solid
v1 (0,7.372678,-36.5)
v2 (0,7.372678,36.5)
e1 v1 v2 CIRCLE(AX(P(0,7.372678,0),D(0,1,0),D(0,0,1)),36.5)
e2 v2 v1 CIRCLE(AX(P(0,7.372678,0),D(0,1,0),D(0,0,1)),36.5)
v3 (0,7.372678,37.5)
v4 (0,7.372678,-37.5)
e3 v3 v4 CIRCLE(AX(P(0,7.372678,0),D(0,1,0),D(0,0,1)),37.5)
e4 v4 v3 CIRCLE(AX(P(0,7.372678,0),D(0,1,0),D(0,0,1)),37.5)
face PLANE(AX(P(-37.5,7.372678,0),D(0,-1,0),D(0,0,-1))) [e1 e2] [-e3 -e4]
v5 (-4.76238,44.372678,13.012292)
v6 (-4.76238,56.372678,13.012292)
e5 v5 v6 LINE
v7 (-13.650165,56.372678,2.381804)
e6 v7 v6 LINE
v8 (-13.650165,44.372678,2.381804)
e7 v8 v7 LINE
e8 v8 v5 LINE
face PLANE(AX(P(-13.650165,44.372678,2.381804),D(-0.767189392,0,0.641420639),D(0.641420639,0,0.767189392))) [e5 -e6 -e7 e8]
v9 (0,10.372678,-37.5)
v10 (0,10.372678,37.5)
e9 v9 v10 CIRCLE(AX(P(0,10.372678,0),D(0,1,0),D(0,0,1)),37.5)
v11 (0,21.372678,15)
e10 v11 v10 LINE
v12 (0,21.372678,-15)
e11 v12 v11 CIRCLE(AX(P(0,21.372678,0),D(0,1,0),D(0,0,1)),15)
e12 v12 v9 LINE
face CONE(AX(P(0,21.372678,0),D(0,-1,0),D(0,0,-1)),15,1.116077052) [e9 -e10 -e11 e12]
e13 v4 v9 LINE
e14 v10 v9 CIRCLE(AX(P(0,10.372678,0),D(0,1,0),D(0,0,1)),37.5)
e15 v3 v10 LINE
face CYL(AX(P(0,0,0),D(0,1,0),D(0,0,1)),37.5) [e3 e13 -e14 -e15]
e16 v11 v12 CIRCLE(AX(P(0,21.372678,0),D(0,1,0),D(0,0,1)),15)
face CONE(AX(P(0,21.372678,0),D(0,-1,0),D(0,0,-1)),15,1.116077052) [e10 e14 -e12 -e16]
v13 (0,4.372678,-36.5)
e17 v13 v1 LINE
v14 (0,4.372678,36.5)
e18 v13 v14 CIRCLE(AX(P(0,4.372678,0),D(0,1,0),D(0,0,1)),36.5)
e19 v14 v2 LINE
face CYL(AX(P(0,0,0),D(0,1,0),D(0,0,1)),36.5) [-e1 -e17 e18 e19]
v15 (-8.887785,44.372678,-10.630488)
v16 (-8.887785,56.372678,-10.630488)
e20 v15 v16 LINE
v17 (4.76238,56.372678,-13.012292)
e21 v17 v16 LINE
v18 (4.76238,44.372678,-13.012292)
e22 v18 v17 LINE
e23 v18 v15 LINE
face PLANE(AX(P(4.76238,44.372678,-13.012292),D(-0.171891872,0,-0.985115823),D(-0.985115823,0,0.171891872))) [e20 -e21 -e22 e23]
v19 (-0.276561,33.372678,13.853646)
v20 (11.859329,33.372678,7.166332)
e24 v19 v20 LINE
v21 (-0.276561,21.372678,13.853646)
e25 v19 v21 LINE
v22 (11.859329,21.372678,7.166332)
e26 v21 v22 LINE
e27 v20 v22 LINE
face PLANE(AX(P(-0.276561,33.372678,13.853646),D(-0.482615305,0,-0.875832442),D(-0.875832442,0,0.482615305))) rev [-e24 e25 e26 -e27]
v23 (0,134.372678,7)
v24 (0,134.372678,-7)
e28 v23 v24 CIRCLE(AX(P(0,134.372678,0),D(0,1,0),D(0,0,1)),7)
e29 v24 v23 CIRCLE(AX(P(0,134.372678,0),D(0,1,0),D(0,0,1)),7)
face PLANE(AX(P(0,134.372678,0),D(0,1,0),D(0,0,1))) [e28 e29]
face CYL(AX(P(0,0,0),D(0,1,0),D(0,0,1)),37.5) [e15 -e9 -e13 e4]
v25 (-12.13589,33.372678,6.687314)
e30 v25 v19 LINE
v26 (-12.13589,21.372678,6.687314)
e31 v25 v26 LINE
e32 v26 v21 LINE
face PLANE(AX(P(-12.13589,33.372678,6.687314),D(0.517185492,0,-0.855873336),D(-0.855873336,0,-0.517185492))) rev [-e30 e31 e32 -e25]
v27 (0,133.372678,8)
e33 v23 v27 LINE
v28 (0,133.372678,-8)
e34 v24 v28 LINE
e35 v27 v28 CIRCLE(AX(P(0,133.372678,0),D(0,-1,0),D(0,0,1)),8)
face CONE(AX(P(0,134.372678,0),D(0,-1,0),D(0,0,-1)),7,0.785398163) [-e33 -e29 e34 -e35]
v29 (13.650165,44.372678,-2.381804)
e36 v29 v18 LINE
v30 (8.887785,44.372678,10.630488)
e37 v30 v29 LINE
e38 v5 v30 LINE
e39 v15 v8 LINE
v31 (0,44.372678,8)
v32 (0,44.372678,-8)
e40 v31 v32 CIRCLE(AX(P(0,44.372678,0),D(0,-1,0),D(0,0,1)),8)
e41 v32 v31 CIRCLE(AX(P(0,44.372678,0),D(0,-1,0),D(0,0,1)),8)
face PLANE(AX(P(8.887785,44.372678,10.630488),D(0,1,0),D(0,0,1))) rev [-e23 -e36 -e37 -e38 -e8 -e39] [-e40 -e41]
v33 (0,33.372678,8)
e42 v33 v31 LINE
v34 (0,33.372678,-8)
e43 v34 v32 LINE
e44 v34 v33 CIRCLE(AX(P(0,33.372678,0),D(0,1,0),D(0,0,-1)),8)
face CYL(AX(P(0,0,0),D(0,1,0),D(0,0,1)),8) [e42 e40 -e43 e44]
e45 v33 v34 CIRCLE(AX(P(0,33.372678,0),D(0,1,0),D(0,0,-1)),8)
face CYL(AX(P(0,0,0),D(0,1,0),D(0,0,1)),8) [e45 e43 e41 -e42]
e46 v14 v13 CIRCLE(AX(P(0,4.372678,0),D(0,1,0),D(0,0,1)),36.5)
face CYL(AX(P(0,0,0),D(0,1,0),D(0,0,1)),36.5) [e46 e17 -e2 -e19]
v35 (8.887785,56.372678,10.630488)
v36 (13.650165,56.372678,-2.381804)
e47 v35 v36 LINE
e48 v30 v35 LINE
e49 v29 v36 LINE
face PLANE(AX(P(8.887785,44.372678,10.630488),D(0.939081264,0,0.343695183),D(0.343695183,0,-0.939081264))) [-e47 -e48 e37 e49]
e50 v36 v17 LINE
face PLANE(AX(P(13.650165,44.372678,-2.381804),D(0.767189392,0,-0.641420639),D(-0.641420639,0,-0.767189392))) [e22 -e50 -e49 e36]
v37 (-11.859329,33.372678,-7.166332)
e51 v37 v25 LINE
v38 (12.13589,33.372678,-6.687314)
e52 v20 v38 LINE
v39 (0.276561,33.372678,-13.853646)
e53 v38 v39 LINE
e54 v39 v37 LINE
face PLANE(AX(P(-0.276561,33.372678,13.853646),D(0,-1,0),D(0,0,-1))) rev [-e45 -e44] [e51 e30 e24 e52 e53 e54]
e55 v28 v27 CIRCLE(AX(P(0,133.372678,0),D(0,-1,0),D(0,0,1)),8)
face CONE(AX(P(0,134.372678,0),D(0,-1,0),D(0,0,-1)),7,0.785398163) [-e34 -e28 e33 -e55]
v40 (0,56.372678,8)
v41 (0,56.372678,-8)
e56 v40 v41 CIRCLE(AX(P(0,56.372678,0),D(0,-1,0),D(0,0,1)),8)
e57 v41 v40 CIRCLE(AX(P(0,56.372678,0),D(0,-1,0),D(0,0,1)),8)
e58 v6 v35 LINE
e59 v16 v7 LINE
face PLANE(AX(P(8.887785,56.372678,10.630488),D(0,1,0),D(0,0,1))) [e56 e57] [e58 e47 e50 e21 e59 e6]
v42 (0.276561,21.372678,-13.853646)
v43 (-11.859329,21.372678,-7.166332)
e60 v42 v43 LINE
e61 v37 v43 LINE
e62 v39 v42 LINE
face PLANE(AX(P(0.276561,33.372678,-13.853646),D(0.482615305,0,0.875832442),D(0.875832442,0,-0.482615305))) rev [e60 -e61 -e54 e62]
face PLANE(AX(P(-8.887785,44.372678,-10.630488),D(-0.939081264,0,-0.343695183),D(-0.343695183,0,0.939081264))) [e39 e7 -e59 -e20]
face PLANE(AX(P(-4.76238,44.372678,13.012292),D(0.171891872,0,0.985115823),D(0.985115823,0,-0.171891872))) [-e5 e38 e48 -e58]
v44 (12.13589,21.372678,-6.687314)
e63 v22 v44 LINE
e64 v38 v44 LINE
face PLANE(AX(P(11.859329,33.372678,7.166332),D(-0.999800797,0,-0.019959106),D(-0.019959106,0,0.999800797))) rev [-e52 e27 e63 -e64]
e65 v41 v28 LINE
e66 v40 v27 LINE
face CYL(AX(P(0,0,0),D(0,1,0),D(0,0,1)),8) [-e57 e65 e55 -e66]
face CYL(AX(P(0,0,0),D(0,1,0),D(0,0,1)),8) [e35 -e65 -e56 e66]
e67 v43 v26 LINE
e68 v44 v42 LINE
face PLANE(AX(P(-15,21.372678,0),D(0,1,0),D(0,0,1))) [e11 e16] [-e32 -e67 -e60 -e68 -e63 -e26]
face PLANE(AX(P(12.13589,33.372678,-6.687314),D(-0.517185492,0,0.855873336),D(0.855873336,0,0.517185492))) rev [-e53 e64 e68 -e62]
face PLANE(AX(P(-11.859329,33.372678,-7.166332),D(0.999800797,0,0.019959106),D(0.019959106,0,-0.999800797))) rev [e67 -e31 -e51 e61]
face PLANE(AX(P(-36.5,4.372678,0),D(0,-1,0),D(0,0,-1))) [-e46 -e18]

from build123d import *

# Parameters (mm, degrees)
EXTRUDE1_DEPTH = 12
EXTRUDE2_START = 35
EXTRUDE2_DEPTH = 12
CHAMFER1_SIZE  = 1


with BuildPart() as part:
    # Sketch1 → Revolve1 (revolve)
    with BuildSketch(Plane.XY, mode=Mode.PRIVATE) as revolve1_sk:
        Polygon((-37.5, 10.372678427), (-15, 21.372678427), (-8, 21.372678427), (-8, 134.372678427), (0, 134.372678427), (0, 4.372678427), (-36.5, 4.372678427), (-36.5, 7.372678427), (-37.5, 7.372678427), align=None)
    revolve(revolve1_sk.sketch.rotate(Axis((0, 0, 0), (0, -1, 0)), 270), axis=Axis((0, 0, 0), (0, -1, 0)))

    # Sketch2 → Extrude1 (add)
    with BuildSketch(Plane(origin=(0, 21.372678427, 0), x_dir=(-1, 0, 0), z_dir=(0, 1, 0))):
        Polygon((-11.859328821, 7.166332389), (-12.135890312, -6.687313836), (-0.27656149, -13.853646226), (11.859328821, -7.166332389), (12.135890312, 6.687313836), (0.27656149, 13.853646226), align=None)
    extrude(amount=EXTRUDE1_DEPTH)

    # Sketch3 → Extrude2 (add)
    with BuildSketch(Plane(origin=(0, 21.372678427, 0), x_dir=(-1, 0, 0), z_dir=(0, 1, 0)).offset(EXTRUDE2_START)):
        Polygon((-8.887785091, 10.63048805), (-13.650165251, -2.381803647), (-4.76238016, -13.012291697), (8.887785091, -10.63048805), (13.650165251, 2.381803647), (4.76238016, 13.012291697), align=None)
    extrude(amount=-EXTRUDE2_DEPTH)

    # Chamfer1
    chamfer1_edges = [part.edges().sort_by_distance(p)[0] for p in [
        (0, 134.372678427, -8),
    ]]
    chamfer(chamfer1_edges, length=CHAMFER1_SIZE)


solid = part.part
